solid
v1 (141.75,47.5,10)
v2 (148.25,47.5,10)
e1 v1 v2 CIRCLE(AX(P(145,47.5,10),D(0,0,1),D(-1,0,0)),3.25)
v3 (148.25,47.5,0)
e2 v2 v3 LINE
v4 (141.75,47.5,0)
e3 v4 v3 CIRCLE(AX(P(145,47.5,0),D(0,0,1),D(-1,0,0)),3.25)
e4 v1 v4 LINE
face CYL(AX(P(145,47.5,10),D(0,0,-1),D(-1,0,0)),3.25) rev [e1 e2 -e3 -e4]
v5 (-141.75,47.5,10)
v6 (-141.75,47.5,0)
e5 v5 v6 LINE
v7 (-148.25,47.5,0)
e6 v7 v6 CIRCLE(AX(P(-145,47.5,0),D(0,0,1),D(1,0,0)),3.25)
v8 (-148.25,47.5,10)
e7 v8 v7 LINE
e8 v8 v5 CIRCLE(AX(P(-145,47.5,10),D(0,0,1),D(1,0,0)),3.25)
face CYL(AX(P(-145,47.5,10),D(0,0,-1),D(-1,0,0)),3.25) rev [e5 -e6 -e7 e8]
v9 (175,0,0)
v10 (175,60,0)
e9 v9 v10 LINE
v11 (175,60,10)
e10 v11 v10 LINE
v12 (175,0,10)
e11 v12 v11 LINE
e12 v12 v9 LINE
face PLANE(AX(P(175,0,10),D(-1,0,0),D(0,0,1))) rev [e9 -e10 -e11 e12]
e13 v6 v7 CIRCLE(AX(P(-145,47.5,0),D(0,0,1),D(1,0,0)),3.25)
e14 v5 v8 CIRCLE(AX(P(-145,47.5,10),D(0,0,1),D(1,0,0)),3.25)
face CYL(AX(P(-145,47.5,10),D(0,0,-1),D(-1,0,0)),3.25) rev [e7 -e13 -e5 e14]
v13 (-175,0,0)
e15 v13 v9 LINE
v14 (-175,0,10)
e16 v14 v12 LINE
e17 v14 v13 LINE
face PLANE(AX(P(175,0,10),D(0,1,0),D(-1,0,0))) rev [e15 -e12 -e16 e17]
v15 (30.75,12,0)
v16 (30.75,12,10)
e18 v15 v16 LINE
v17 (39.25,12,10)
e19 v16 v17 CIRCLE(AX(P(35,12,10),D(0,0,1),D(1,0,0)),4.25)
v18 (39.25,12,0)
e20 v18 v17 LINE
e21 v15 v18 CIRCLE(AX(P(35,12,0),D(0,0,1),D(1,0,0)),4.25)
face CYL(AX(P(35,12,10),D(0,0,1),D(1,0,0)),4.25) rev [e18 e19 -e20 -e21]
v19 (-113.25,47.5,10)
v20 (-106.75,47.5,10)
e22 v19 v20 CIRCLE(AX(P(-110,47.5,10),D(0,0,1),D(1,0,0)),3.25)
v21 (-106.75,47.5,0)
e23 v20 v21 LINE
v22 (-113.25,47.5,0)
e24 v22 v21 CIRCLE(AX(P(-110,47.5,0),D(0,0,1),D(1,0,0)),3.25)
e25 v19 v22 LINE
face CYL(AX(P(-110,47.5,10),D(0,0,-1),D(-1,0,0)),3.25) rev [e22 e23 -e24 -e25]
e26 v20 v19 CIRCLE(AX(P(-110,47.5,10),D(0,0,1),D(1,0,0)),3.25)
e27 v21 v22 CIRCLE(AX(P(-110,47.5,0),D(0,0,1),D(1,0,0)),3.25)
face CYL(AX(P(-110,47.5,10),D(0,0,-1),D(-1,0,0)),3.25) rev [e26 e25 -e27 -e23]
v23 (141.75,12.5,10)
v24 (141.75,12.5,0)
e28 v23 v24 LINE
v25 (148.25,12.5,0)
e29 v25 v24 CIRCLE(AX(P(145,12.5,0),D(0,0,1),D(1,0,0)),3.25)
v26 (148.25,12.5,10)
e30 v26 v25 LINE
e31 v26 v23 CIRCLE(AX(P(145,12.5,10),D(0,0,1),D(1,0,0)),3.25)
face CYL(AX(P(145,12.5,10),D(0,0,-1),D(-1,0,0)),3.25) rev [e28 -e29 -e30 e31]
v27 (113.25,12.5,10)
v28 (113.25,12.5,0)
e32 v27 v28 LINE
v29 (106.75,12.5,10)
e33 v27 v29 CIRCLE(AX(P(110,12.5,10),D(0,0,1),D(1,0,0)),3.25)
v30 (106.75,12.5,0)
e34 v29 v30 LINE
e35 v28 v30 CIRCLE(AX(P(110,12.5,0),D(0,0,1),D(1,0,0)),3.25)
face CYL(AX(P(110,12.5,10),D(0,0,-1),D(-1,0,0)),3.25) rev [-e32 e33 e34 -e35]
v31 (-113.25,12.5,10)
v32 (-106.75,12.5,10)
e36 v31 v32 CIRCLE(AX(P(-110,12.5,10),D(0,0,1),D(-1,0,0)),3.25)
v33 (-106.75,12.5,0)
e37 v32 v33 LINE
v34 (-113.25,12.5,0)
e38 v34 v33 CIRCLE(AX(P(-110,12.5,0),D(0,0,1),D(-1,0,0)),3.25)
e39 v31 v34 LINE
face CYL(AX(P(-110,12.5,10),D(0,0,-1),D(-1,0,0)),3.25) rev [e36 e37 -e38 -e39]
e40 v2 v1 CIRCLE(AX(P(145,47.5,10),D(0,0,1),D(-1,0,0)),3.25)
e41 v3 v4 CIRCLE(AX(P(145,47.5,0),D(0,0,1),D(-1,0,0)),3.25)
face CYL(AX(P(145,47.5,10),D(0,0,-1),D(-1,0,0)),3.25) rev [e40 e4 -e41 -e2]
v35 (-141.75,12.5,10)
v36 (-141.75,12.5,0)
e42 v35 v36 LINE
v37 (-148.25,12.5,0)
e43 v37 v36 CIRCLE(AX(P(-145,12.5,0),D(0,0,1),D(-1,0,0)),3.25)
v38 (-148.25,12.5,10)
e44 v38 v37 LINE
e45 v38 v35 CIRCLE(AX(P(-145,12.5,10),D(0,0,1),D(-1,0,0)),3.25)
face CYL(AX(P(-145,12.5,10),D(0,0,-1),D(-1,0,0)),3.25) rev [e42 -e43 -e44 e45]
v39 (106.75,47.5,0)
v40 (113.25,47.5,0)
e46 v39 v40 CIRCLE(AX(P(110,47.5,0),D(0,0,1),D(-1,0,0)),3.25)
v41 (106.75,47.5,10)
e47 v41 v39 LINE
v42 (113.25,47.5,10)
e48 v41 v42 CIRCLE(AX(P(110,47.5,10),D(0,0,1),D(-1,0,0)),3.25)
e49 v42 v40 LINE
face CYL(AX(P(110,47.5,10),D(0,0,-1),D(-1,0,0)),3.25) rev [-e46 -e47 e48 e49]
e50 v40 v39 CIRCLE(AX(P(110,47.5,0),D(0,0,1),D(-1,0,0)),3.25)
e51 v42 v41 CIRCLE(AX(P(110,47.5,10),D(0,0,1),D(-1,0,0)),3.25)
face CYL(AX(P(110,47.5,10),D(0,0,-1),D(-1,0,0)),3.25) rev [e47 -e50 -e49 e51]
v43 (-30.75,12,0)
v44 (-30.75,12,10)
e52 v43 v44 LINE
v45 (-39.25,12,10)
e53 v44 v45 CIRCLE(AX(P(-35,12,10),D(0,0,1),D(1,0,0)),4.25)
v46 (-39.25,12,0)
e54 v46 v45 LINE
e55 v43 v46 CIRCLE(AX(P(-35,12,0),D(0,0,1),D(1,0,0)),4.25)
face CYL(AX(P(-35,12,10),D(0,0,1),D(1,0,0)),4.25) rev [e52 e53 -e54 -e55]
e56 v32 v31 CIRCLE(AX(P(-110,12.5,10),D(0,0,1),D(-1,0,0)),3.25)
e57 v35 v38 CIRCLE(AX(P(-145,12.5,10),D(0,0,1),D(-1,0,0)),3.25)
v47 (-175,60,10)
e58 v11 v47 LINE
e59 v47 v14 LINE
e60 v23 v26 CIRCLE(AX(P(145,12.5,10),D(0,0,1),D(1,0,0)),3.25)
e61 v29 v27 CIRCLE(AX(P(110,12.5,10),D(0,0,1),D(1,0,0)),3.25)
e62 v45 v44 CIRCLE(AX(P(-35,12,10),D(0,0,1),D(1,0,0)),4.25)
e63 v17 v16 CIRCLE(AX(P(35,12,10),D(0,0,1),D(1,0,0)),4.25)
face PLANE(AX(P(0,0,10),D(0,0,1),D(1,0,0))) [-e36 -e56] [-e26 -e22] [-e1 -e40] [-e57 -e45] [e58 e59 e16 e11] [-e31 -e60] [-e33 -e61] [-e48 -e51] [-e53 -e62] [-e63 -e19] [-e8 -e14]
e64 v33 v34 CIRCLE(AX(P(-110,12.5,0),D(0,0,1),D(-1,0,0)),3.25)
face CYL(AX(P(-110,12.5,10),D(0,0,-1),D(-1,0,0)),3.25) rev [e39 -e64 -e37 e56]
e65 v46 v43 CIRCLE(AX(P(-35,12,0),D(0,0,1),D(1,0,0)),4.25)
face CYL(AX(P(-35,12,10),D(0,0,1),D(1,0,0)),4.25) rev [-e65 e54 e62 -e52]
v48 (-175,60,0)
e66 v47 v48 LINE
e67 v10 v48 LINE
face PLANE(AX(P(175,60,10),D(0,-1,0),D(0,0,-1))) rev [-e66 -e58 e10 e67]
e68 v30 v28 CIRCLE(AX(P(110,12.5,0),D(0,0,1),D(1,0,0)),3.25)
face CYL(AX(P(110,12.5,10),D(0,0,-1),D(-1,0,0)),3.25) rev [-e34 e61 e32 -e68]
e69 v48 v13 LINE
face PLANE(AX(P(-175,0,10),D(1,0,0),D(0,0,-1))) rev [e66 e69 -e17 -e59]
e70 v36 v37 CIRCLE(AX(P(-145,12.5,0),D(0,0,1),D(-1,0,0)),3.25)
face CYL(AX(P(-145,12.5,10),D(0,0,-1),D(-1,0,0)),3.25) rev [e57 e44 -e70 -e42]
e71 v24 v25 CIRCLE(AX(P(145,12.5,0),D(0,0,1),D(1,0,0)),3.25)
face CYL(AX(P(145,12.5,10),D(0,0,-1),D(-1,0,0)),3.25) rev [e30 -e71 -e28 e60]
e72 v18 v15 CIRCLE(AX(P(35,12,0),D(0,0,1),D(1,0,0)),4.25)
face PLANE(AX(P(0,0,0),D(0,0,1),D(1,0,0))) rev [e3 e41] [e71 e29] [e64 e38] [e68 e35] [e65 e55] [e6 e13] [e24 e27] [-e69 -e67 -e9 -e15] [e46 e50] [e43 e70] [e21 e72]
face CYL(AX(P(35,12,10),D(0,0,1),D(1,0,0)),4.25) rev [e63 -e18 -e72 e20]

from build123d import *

# Parameters (mm, degrees)
SKETCH1_W           = 350
SKETCH1_H           = 60
SKETCH1_R           = 3.25
BOSS_EXTRUDE1_DEPTH = 10
M10_TAPPED_HOLE1_D  = 8.5


with BuildPart() as part:
    # Sketch1 → Boss-Extrude1 (new body)
    with BuildSketch(Plane.XY):
        with Locations((0, 30)):
            Rectangle(SKETCH1_W, SKETCH1_H)
        with Locations((-145, 47.5)):
            Circle(SKETCH1_R, mode=Mode.SUBTRACT)
        with Locations((-110, 47.5)):
            Circle(SKETCH1_R, mode=Mode.SUBTRACT)
        with Locations(Location((-110, 12.5, 0), (0, 0, 180))):
            Circle(SKETCH1_R, mode=Mode.SUBTRACT)
        with Locations(Location((-145, 12.5, 0), (0, 0, 180))):
            Circle(SKETCH1_R, mode=Mode.SUBTRACT)
        with Locations((110, 12.5)):
            Circle(SKETCH1_R, mode=Mode.SUBTRACT)
        with Locations((145, 12.5)):
            Circle(SKETCH1_R, mode=Mode.SUBTRACT)
        with Locations(Location((110, 47.5, 0), (0, 0, 180))):
            Circle(SKETCH1_R, mode=Mode.SUBTRACT)
        with Locations(Location((145, 47.5, 0), (0, 0, 180))):
            Circle(SKETCH1_R, mode=Mode.SUBTRACT)
    extrude(amount=BOSS_EXTRUDE1_DEPTH)

    # M10 Tapped Hole1 (through all)
    with Locations(Plane.XY.offset(10)):
        with Locations((-35, 12), (35, 12)):
            Hole(M10_TAPPED_HOLE1_D / 2)


solid = part.part
